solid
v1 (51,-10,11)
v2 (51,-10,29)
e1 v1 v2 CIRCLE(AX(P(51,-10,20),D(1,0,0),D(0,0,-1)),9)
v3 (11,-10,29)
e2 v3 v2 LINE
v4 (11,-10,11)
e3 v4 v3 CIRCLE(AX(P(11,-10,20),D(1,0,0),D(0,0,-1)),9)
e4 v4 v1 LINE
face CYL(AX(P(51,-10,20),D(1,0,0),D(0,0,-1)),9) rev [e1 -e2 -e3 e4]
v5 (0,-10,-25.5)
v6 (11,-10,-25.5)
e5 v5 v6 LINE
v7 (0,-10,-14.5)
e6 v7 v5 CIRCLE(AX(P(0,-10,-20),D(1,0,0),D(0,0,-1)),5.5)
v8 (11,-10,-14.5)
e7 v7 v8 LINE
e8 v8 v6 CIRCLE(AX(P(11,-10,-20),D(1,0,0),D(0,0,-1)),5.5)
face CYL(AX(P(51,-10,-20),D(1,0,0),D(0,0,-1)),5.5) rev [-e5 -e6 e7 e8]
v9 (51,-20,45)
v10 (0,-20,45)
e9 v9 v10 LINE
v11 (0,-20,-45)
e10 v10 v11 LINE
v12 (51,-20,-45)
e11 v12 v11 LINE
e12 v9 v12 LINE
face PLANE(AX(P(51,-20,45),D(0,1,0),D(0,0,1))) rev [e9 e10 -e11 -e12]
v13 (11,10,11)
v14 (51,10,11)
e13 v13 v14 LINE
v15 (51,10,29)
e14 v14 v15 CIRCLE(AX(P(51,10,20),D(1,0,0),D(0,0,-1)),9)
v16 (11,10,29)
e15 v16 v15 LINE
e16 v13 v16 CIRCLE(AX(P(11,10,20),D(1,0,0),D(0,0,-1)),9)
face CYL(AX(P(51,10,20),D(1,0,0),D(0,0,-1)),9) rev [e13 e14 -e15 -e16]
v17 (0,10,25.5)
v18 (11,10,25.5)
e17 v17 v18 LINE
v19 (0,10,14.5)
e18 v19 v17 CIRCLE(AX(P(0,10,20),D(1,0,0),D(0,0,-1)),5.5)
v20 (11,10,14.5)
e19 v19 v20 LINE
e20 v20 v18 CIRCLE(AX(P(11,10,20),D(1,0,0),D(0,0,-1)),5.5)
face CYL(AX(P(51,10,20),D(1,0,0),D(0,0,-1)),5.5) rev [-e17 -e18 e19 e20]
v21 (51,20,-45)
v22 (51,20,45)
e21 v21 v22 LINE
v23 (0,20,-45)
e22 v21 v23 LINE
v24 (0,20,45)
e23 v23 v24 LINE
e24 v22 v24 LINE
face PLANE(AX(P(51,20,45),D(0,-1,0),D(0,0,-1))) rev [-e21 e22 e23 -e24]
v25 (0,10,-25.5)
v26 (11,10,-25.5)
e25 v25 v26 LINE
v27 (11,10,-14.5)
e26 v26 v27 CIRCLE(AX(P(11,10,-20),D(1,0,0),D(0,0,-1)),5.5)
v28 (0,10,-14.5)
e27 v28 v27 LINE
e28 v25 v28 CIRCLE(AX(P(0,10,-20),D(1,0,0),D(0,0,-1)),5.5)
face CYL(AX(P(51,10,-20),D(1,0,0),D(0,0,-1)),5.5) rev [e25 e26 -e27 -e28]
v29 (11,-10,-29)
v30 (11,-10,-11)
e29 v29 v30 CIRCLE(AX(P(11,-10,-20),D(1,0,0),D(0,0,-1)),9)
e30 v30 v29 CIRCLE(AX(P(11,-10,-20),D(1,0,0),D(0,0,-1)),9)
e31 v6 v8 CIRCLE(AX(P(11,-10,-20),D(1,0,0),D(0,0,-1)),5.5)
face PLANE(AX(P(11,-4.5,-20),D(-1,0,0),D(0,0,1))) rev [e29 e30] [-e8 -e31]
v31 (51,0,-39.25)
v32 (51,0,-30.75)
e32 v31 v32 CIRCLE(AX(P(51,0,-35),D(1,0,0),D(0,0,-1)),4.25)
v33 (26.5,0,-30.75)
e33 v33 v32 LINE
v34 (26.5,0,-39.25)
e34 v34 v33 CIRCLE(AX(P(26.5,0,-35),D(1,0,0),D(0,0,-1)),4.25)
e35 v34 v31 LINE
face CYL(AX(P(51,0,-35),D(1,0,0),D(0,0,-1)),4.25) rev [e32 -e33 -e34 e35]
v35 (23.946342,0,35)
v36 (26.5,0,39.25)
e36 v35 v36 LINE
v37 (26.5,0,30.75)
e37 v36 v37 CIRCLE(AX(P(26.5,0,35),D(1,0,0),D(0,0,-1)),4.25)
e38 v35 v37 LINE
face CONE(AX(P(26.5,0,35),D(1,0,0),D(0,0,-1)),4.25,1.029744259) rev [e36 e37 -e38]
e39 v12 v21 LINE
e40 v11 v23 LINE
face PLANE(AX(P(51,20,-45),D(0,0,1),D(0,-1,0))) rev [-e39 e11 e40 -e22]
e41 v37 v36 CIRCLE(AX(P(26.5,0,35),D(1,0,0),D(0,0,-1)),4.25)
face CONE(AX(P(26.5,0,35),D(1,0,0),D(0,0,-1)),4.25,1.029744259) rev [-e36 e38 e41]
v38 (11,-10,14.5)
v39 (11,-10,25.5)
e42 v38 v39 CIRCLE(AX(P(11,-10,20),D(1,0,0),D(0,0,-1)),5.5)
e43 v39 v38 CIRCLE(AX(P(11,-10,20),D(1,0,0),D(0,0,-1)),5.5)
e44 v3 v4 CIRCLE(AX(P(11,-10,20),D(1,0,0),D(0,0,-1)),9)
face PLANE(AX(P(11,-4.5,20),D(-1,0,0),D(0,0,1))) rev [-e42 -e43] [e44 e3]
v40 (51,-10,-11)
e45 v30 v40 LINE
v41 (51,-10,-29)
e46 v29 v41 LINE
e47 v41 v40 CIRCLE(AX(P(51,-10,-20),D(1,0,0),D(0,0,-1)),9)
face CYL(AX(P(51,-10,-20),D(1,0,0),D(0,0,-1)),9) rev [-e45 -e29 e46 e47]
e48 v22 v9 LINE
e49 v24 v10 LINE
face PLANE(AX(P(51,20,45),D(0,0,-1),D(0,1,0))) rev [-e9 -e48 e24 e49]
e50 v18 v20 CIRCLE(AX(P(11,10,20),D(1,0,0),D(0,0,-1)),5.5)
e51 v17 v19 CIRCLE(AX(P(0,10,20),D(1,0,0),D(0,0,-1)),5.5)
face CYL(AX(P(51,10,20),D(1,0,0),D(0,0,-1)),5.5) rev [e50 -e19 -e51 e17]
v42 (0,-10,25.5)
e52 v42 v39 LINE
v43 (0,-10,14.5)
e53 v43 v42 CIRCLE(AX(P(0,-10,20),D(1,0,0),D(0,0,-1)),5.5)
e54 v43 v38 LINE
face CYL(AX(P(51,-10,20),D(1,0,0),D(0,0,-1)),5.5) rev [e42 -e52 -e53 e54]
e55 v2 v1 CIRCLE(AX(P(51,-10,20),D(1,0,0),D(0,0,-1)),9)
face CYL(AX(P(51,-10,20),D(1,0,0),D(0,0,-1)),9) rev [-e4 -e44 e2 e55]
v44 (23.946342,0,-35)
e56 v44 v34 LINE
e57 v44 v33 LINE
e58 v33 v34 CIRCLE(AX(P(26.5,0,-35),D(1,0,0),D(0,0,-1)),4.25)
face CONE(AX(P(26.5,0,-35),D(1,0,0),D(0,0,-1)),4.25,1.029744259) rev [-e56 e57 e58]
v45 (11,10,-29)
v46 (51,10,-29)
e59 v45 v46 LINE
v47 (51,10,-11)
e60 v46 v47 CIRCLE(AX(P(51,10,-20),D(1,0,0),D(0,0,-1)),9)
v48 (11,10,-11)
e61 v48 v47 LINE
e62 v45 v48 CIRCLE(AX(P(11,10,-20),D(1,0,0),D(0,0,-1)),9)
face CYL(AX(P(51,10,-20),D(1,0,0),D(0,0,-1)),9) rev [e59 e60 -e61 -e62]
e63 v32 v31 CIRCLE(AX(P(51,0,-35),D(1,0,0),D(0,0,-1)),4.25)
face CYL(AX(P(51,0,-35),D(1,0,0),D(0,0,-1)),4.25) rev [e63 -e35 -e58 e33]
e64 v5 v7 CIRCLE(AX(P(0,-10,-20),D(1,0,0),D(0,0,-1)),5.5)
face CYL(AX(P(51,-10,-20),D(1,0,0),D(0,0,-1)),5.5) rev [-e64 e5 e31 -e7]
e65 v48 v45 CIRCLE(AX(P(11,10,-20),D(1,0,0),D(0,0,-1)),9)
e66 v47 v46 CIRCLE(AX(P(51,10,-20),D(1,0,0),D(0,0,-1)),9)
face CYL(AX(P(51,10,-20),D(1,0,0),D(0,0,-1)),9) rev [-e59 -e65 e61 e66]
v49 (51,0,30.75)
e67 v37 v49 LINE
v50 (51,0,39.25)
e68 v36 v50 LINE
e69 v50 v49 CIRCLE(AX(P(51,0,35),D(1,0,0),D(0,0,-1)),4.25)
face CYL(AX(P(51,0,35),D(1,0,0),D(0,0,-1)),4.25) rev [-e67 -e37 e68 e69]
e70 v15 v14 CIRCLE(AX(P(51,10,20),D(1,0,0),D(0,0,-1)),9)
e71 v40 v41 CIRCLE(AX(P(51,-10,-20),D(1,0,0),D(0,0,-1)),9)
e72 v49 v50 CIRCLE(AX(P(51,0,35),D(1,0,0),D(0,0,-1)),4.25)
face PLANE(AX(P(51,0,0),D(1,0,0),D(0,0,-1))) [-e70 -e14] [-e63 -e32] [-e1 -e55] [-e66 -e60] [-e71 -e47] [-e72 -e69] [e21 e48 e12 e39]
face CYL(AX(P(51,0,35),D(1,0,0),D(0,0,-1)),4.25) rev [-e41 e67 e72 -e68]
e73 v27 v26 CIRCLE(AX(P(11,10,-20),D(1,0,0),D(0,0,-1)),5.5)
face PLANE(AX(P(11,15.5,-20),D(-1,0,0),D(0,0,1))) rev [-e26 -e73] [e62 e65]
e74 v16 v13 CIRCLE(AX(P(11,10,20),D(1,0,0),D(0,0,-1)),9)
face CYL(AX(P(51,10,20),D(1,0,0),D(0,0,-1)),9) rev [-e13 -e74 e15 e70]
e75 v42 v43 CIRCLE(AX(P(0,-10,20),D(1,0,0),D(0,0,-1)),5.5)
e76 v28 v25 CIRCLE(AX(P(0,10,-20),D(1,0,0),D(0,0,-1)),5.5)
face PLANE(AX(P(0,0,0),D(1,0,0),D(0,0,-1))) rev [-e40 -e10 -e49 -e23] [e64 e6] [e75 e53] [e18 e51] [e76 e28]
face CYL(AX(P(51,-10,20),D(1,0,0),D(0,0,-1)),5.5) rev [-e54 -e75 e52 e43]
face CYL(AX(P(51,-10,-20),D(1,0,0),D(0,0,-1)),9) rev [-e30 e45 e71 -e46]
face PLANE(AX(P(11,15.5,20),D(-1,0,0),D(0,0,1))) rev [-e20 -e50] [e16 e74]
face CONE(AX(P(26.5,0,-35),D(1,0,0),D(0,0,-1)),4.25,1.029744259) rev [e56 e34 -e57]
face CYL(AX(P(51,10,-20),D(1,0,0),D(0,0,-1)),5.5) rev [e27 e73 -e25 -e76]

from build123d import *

# Parameters (mm, degrees)
SKETCH_1_W                = 90
SKETCH_1_H                = 40
EXTRUDE_1_DEPTH           = 51
HOLE_WIZARD_1_D           = 11
HOLE_WIZARD_1_CBORE_D     = 18
HOLE_WIZARD_1_CBORE_DEPTH = 40
HOLE_WIZARD_M10_1_D       = 8.5
HOLE_WIZARD_M10_1_DEPTH   = 24.5
HOLE_WIZARD_M10_1_TIP     = 2.553657631


with BuildPart() as part:
    # 草图1 → 凸台-拉伸1 (new body)
    with BuildSketch(Plane(origin=(0, 0, 0), x_dir=(0, 0, -1), z_dir=(1, 0, 0))):
        Rectangle(SKETCH_1_W, SKETCH_1_H)
    extrude(amount=EXTRUDE_1_DEPTH)

    # 打孔尺寸(%根据)内六角圆柱头螺钉的类型1 (through all)
    with Locations(Plane(origin=(51, 0, 0), x_dir=(0, 0, -1), z_dir=(1, 0, 0))):
        with Locations((-20, 10), (20, 10), (-20, -10), (20, -10)):
            CounterBoreHole(HOLE_WIZARD_1_D / 2, HOLE_WIZARD_1_CBORE_D / 2, HOLE_WIZARD_1_CBORE_DEPTH)

    # M10 螺纹孔1
    with Locations(Plane(origin=(51, 0, 0), x_dir=(0, 0, -1), z_dir=(1, 0, 0))):
        with Locations((-35, 0), (35, 0)):
            Hole(HOLE_WIZARD_M10_1_D / 2, depth=HOLE_WIZARD_M10_1_DEPTH)
            with Locations((0, 0, -(HOLE_WIZARD_M10_1_DEPTH + HOLE_WIZARD_M10_1_TIP / 2))):  # 118° drill point
                Cone(0, HOLE_WIZARD_M10_1_D / 2, HOLE_WIZARD_M10_1_TIP, mode=Mode.SUBTRACT)


solid = part.part
